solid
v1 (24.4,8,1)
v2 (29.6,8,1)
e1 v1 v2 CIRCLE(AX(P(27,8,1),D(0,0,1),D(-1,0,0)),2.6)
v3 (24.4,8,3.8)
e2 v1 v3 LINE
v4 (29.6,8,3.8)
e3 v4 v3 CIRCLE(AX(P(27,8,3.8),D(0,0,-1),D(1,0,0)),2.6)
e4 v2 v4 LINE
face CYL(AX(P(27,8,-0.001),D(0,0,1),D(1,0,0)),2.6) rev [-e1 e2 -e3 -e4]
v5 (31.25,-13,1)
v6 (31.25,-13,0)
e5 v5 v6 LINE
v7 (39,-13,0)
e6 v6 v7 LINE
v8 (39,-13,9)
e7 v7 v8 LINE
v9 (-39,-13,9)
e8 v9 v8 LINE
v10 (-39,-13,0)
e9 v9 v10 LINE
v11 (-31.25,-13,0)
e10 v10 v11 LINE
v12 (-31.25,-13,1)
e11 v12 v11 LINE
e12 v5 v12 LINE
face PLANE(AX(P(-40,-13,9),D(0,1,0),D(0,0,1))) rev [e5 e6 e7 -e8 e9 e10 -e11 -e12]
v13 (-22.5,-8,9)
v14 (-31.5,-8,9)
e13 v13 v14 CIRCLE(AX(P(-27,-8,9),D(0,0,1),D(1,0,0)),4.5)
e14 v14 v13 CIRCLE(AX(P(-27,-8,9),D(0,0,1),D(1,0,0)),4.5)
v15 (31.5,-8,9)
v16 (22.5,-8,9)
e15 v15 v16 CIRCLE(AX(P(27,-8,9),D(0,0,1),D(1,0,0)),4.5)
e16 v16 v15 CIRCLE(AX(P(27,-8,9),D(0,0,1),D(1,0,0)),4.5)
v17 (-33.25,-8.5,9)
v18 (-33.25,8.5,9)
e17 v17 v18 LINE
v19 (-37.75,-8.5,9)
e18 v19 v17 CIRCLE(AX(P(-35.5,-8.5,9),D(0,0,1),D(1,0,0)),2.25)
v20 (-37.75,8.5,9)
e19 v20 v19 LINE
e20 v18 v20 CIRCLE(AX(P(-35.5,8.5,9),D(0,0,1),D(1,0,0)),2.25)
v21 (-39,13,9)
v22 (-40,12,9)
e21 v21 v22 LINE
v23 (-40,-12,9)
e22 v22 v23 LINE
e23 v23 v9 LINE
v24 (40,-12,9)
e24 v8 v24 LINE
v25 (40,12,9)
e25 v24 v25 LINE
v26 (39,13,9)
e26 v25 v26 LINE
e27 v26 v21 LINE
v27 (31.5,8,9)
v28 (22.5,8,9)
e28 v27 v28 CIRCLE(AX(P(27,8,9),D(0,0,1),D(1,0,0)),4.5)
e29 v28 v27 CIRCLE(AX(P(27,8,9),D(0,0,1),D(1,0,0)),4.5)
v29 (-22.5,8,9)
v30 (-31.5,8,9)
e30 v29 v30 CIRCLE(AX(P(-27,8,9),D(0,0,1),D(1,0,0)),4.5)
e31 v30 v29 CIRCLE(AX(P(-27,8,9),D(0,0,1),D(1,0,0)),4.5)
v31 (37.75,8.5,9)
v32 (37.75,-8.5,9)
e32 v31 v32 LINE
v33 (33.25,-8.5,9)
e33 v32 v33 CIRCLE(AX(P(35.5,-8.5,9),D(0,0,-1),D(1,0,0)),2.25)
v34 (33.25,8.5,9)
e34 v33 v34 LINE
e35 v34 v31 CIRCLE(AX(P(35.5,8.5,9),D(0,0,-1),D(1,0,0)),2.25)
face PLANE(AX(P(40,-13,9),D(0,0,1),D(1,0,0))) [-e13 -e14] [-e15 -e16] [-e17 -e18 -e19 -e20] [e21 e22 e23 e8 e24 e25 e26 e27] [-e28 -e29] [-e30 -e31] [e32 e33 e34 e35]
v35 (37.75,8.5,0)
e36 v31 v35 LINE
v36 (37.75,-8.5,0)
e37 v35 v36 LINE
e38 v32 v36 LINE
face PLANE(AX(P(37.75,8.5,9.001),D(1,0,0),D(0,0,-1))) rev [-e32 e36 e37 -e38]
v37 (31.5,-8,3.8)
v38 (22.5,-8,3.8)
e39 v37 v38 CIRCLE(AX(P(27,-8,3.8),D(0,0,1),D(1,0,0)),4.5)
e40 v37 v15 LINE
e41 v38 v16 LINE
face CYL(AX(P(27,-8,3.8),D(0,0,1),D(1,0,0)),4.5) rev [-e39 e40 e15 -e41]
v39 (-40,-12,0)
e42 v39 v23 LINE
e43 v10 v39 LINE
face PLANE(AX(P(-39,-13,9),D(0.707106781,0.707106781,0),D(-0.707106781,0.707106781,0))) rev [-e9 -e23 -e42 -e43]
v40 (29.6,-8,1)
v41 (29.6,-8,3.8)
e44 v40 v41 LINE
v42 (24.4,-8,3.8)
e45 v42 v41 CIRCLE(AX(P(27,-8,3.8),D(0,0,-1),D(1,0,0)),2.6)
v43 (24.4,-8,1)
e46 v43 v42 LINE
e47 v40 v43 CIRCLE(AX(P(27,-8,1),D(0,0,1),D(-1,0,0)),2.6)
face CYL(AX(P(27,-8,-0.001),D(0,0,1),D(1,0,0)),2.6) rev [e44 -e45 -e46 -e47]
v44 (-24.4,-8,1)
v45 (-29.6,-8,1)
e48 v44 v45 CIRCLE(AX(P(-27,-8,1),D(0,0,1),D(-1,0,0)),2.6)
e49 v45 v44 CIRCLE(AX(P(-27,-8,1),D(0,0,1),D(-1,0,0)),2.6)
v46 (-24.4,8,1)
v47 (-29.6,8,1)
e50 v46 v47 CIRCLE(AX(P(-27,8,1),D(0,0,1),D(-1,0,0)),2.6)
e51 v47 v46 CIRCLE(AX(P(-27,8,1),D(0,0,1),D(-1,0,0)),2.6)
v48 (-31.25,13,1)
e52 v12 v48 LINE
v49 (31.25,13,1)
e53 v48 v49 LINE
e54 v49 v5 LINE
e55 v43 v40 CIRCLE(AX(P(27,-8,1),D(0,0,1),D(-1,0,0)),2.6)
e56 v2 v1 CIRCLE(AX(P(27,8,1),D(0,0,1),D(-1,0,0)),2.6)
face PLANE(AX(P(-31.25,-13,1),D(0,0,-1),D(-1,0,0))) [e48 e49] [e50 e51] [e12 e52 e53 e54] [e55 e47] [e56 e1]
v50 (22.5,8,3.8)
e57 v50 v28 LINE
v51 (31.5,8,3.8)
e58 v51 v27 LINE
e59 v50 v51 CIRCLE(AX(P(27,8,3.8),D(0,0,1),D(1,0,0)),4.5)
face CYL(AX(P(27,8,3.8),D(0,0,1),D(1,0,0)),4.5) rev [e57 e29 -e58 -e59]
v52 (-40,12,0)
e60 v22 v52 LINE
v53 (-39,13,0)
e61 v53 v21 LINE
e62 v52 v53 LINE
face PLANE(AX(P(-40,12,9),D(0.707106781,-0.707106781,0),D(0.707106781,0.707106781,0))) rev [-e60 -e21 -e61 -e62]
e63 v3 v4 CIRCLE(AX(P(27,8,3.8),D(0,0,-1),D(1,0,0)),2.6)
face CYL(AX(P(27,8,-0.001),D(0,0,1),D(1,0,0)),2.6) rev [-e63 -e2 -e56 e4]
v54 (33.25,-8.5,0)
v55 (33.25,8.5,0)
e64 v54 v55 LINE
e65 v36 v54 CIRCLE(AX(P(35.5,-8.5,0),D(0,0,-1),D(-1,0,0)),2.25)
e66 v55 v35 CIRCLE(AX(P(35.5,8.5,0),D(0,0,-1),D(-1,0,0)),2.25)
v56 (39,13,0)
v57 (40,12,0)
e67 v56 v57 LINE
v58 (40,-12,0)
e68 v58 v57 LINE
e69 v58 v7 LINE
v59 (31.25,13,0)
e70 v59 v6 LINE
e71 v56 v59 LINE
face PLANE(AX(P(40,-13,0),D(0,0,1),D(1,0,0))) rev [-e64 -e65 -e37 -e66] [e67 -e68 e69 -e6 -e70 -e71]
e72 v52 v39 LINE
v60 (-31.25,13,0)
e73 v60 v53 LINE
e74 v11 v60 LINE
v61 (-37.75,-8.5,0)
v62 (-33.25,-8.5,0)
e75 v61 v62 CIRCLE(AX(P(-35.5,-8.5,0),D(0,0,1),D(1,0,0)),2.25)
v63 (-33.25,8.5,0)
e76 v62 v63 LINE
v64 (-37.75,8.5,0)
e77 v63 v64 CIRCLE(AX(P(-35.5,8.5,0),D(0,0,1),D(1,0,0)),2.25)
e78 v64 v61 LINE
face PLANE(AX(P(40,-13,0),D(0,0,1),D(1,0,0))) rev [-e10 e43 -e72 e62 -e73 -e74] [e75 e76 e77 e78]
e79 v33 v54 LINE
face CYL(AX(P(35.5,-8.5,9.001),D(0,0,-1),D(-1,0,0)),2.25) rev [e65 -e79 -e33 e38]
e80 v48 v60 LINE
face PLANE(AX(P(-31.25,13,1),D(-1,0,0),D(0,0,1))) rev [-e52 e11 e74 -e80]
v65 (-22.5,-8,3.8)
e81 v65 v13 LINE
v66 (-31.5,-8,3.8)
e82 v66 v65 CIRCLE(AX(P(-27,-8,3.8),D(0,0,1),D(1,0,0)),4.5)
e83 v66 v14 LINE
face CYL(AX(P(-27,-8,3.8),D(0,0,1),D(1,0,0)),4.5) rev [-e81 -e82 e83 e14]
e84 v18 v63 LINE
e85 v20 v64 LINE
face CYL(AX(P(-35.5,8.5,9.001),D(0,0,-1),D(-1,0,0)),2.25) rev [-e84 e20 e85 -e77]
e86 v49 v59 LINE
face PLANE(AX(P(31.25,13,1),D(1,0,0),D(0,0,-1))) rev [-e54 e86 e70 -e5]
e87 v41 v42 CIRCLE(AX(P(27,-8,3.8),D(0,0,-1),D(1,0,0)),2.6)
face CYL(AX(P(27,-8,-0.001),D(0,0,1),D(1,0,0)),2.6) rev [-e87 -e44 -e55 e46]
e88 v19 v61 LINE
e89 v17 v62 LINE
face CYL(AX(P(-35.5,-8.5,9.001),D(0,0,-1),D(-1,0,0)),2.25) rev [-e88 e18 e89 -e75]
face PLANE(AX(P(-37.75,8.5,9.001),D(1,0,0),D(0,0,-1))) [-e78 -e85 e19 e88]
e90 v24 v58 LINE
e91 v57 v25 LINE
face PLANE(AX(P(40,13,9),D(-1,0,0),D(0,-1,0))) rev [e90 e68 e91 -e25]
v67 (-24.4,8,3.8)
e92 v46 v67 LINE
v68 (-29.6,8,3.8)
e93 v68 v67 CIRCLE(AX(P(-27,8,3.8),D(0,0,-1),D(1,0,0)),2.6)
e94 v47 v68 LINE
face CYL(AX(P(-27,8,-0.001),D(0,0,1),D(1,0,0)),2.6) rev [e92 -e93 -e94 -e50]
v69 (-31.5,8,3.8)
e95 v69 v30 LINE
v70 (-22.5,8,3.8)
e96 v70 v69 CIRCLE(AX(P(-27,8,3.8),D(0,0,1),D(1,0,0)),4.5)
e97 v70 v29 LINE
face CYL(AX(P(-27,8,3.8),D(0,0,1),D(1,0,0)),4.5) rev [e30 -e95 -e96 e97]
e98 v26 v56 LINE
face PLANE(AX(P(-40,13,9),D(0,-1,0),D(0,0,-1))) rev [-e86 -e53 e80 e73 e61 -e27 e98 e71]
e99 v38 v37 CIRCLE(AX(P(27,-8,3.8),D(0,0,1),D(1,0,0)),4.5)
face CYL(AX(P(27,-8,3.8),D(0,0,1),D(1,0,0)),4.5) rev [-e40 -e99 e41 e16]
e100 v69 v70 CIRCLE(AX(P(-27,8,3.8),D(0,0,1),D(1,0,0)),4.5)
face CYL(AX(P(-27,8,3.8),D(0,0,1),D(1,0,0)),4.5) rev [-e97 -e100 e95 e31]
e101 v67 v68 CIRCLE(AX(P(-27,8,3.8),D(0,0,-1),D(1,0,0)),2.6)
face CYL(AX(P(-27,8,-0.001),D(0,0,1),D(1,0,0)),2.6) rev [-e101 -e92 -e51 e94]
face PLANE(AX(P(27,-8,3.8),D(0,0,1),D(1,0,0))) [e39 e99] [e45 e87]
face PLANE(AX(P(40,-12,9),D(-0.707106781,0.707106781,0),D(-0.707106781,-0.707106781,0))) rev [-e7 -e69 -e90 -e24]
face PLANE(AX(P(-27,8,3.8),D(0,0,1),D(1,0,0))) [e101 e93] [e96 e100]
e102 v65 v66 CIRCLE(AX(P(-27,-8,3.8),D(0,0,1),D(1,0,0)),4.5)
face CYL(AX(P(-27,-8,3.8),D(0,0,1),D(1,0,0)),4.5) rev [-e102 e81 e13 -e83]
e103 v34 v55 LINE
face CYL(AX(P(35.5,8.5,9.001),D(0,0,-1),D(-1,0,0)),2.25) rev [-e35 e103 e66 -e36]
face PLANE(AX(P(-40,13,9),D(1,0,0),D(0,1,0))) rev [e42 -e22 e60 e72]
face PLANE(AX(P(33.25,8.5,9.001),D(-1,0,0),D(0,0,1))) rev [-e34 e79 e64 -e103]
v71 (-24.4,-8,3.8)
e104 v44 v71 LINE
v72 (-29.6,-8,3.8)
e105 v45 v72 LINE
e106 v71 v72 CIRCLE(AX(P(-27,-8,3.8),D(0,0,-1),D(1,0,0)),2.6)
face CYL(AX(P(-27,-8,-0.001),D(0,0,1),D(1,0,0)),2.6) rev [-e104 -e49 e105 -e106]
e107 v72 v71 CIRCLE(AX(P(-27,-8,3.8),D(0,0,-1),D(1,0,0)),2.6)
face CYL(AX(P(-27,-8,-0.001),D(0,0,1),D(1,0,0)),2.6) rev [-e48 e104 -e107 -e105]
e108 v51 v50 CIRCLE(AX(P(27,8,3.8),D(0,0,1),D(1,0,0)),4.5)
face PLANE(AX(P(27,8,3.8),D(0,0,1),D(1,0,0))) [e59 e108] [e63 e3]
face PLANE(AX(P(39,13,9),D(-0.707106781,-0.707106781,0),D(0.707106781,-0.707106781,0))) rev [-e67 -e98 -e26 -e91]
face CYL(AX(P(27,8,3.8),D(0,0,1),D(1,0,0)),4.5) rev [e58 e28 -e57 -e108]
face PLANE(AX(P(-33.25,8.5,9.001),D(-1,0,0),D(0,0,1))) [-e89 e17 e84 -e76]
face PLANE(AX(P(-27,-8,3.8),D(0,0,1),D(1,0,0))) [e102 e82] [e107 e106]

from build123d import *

# Parameters (mm, degrees)
SKETCH1_W           = 80
SKETCH1_H           = 26
BOSS_EXTRUDE1_DEPTH = 9
CUT_EXTRUDE1_REACH  = 45.012
SKETCH2_R           = 2.6
SKETCH3_R           = 4.5
CUT_EXTRUDE2_DEPTH  = 5.2
CUT_EXTRUDE3_REACH  = 45.012
SKETCH8_W           = 62.5
SKETCH8_H           = 26
CUT_EXTRUDE5_DEPTH  = 1
CHAMFER1_SIZE       = 1


with BuildPart() as part:
    # Sketch1 → Boss-Extrude1 (new body)
    with BuildSketch(Plane.XY):
        Rectangle(SKETCH1_W, SKETCH1_H)
    extrude(amount=BOSS_EXTRUDE1_DEPTH)

    # Sketch2 → Cut-Extrude1 (cut, up to next)
    with BuildSketch(Plane.XY.offset(9), mode=Mode.PRIVATE) as cut_extrude1_sk1:
        with Locations((-27, -8)):
            Circle(SKETCH2_R)
    cut_extrude1_tool1 = extrude(cut_extrude1_sk1.sketch, amount=-CUT_EXTRUDE1_REACH, mode=Mode.PRIVATE) & part.part
    # Sketch2 → Cut-Extrude1 (cut, up to next)
    with BuildSketch(Plane.XY.offset(9), mode=Mode.PRIVATE) as cut_extrude1_sk2:
        with Locations((-27, 8)):
            Circle(SKETCH2_R)
    cut_extrude1_tool2 = extrude(cut_extrude1_sk2.sketch, amount=-CUT_EXTRUDE1_REACH, mode=Mode.PRIVATE) & part.part
    # Sketch2 → Cut-Extrude1 (cut, up to next)
    with BuildSketch(Plane.XY.offset(9), mode=Mode.PRIVATE) as cut_extrude1_sk3:
        with Locations((27, 8)):
            Circle(SKETCH2_R)
    cut_extrude1_tool3 = extrude(cut_extrude1_sk3.sketch, amount=-CUT_EXTRUDE1_REACH, mode=Mode.PRIVATE) & part.part
    # Sketch2 → Cut-Extrude1 (cut, up to next)
    with BuildSketch(Plane.XY.offset(9), mode=Mode.PRIVATE) as cut_extrude1_sk4:
        with Locations((27, -8)):
            Circle(SKETCH2_R)
    cut_extrude1_tool4 = extrude(cut_extrude1_sk4.sketch, amount=-CUT_EXTRUDE1_REACH, mode=Mode.PRIVATE) & part.part
    add(cut_extrude1_tool1.solids().sort_by_distance((-27, -8, 9))[0], mode=Mode.SUBTRACT)
    add(cut_extrude1_tool2.solids().sort_by_distance((-27, 8, 9))[0], mode=Mode.SUBTRACT)
    add(cut_extrude1_tool3.solids().sort_by_distance((27, 8, 9))[0], mode=Mode.SUBTRACT)
    add(cut_extrude1_tool4.solids().sort_by_distance((27, -8, 9))[0], mode=Mode.SUBTRACT)

    # Sketch3 → Cut-Extrude2 (cut)
    with BuildSketch(Plane.XY.offset(9)):
        with Locations((-27, -8)):
            Circle(SKETCH3_R)
        with Locations((-27, 8)):
            Circle(SKETCH3_R)
        with Locations((27, 8)):
            Circle(SKETCH3_R)
        with Locations((27, -8)):
            Circle(SKETCH3_R)
    extrude(amount=-CUT_EXTRUDE2_DEPTH, mode=Mode.SUBTRACT)

    # Sketch6 → Cut-Extrude3 (cut, up to next)
    with BuildSketch(Plane(origin=(0, 0, 0), x_dir=(-1, 0, 0), z_dir=(0, 0, -1)), mode=Mode.PRIVATE) as cut_extrude3_sk1:
        with BuildLine():
            Line((-33.25, 8.5), (-33.25, -8.5))
            ThreePointArc((-33.25, -8.5), (-35.5, -10.75), (-37.75, -8.5))
            Line((-37.75, -8.5), (-37.75, 8.5))
            ThreePointArc((-37.75, 8.5), (-35.5, 10.75), (-33.25, 8.5))
        make_face()
    cut_extrude3_tool1 = extrude(cut_extrude3_sk1.sketch, amount=-CUT_EXTRUDE3_REACH, mode=Mode.PRIVATE) & part.part
    cut_extrude3 = cut_extrude3_tool1.solids().sort_by_distance((35.5, 0, 0))[0]
    add(cut_extrude3, mode=Mode.SUBTRACT)

    # Mirror1: Cut-Extrude3 across plane
    add(cut_extrude3.mirror(Plane(origin=(0, 0, 0), x_dir=(0, 0, 1), z_dir=(1, 0, 0))), mode=Mode.SUBTRACT)

    # Sketch8 → Cut-Extrude5 (cut)
    with BuildSketch(Plane(origin=(0, 0, 0), x_dir=(-1, 0, 0), z_dir=(0, 0, -1))):
        Rectangle(SKETCH8_W, SKETCH8_H)
    extrude(amount=-CUT_EXTRUDE5_DEPTH, mode=Mode.SUBTRACT)

    # Chamfer1
    chamfer1_edges = [part.edges().sort_by_distance(p)[0] for p in [
        (40, -13, 4.5),
        (-40, -13, 4.5),
        (-40, 13, 4.5),
        (40, 13, 4.5),
    ]]
    chamfer(chamfer1_edges, length=CHAMFER1_SIZE)


solid = part.part
